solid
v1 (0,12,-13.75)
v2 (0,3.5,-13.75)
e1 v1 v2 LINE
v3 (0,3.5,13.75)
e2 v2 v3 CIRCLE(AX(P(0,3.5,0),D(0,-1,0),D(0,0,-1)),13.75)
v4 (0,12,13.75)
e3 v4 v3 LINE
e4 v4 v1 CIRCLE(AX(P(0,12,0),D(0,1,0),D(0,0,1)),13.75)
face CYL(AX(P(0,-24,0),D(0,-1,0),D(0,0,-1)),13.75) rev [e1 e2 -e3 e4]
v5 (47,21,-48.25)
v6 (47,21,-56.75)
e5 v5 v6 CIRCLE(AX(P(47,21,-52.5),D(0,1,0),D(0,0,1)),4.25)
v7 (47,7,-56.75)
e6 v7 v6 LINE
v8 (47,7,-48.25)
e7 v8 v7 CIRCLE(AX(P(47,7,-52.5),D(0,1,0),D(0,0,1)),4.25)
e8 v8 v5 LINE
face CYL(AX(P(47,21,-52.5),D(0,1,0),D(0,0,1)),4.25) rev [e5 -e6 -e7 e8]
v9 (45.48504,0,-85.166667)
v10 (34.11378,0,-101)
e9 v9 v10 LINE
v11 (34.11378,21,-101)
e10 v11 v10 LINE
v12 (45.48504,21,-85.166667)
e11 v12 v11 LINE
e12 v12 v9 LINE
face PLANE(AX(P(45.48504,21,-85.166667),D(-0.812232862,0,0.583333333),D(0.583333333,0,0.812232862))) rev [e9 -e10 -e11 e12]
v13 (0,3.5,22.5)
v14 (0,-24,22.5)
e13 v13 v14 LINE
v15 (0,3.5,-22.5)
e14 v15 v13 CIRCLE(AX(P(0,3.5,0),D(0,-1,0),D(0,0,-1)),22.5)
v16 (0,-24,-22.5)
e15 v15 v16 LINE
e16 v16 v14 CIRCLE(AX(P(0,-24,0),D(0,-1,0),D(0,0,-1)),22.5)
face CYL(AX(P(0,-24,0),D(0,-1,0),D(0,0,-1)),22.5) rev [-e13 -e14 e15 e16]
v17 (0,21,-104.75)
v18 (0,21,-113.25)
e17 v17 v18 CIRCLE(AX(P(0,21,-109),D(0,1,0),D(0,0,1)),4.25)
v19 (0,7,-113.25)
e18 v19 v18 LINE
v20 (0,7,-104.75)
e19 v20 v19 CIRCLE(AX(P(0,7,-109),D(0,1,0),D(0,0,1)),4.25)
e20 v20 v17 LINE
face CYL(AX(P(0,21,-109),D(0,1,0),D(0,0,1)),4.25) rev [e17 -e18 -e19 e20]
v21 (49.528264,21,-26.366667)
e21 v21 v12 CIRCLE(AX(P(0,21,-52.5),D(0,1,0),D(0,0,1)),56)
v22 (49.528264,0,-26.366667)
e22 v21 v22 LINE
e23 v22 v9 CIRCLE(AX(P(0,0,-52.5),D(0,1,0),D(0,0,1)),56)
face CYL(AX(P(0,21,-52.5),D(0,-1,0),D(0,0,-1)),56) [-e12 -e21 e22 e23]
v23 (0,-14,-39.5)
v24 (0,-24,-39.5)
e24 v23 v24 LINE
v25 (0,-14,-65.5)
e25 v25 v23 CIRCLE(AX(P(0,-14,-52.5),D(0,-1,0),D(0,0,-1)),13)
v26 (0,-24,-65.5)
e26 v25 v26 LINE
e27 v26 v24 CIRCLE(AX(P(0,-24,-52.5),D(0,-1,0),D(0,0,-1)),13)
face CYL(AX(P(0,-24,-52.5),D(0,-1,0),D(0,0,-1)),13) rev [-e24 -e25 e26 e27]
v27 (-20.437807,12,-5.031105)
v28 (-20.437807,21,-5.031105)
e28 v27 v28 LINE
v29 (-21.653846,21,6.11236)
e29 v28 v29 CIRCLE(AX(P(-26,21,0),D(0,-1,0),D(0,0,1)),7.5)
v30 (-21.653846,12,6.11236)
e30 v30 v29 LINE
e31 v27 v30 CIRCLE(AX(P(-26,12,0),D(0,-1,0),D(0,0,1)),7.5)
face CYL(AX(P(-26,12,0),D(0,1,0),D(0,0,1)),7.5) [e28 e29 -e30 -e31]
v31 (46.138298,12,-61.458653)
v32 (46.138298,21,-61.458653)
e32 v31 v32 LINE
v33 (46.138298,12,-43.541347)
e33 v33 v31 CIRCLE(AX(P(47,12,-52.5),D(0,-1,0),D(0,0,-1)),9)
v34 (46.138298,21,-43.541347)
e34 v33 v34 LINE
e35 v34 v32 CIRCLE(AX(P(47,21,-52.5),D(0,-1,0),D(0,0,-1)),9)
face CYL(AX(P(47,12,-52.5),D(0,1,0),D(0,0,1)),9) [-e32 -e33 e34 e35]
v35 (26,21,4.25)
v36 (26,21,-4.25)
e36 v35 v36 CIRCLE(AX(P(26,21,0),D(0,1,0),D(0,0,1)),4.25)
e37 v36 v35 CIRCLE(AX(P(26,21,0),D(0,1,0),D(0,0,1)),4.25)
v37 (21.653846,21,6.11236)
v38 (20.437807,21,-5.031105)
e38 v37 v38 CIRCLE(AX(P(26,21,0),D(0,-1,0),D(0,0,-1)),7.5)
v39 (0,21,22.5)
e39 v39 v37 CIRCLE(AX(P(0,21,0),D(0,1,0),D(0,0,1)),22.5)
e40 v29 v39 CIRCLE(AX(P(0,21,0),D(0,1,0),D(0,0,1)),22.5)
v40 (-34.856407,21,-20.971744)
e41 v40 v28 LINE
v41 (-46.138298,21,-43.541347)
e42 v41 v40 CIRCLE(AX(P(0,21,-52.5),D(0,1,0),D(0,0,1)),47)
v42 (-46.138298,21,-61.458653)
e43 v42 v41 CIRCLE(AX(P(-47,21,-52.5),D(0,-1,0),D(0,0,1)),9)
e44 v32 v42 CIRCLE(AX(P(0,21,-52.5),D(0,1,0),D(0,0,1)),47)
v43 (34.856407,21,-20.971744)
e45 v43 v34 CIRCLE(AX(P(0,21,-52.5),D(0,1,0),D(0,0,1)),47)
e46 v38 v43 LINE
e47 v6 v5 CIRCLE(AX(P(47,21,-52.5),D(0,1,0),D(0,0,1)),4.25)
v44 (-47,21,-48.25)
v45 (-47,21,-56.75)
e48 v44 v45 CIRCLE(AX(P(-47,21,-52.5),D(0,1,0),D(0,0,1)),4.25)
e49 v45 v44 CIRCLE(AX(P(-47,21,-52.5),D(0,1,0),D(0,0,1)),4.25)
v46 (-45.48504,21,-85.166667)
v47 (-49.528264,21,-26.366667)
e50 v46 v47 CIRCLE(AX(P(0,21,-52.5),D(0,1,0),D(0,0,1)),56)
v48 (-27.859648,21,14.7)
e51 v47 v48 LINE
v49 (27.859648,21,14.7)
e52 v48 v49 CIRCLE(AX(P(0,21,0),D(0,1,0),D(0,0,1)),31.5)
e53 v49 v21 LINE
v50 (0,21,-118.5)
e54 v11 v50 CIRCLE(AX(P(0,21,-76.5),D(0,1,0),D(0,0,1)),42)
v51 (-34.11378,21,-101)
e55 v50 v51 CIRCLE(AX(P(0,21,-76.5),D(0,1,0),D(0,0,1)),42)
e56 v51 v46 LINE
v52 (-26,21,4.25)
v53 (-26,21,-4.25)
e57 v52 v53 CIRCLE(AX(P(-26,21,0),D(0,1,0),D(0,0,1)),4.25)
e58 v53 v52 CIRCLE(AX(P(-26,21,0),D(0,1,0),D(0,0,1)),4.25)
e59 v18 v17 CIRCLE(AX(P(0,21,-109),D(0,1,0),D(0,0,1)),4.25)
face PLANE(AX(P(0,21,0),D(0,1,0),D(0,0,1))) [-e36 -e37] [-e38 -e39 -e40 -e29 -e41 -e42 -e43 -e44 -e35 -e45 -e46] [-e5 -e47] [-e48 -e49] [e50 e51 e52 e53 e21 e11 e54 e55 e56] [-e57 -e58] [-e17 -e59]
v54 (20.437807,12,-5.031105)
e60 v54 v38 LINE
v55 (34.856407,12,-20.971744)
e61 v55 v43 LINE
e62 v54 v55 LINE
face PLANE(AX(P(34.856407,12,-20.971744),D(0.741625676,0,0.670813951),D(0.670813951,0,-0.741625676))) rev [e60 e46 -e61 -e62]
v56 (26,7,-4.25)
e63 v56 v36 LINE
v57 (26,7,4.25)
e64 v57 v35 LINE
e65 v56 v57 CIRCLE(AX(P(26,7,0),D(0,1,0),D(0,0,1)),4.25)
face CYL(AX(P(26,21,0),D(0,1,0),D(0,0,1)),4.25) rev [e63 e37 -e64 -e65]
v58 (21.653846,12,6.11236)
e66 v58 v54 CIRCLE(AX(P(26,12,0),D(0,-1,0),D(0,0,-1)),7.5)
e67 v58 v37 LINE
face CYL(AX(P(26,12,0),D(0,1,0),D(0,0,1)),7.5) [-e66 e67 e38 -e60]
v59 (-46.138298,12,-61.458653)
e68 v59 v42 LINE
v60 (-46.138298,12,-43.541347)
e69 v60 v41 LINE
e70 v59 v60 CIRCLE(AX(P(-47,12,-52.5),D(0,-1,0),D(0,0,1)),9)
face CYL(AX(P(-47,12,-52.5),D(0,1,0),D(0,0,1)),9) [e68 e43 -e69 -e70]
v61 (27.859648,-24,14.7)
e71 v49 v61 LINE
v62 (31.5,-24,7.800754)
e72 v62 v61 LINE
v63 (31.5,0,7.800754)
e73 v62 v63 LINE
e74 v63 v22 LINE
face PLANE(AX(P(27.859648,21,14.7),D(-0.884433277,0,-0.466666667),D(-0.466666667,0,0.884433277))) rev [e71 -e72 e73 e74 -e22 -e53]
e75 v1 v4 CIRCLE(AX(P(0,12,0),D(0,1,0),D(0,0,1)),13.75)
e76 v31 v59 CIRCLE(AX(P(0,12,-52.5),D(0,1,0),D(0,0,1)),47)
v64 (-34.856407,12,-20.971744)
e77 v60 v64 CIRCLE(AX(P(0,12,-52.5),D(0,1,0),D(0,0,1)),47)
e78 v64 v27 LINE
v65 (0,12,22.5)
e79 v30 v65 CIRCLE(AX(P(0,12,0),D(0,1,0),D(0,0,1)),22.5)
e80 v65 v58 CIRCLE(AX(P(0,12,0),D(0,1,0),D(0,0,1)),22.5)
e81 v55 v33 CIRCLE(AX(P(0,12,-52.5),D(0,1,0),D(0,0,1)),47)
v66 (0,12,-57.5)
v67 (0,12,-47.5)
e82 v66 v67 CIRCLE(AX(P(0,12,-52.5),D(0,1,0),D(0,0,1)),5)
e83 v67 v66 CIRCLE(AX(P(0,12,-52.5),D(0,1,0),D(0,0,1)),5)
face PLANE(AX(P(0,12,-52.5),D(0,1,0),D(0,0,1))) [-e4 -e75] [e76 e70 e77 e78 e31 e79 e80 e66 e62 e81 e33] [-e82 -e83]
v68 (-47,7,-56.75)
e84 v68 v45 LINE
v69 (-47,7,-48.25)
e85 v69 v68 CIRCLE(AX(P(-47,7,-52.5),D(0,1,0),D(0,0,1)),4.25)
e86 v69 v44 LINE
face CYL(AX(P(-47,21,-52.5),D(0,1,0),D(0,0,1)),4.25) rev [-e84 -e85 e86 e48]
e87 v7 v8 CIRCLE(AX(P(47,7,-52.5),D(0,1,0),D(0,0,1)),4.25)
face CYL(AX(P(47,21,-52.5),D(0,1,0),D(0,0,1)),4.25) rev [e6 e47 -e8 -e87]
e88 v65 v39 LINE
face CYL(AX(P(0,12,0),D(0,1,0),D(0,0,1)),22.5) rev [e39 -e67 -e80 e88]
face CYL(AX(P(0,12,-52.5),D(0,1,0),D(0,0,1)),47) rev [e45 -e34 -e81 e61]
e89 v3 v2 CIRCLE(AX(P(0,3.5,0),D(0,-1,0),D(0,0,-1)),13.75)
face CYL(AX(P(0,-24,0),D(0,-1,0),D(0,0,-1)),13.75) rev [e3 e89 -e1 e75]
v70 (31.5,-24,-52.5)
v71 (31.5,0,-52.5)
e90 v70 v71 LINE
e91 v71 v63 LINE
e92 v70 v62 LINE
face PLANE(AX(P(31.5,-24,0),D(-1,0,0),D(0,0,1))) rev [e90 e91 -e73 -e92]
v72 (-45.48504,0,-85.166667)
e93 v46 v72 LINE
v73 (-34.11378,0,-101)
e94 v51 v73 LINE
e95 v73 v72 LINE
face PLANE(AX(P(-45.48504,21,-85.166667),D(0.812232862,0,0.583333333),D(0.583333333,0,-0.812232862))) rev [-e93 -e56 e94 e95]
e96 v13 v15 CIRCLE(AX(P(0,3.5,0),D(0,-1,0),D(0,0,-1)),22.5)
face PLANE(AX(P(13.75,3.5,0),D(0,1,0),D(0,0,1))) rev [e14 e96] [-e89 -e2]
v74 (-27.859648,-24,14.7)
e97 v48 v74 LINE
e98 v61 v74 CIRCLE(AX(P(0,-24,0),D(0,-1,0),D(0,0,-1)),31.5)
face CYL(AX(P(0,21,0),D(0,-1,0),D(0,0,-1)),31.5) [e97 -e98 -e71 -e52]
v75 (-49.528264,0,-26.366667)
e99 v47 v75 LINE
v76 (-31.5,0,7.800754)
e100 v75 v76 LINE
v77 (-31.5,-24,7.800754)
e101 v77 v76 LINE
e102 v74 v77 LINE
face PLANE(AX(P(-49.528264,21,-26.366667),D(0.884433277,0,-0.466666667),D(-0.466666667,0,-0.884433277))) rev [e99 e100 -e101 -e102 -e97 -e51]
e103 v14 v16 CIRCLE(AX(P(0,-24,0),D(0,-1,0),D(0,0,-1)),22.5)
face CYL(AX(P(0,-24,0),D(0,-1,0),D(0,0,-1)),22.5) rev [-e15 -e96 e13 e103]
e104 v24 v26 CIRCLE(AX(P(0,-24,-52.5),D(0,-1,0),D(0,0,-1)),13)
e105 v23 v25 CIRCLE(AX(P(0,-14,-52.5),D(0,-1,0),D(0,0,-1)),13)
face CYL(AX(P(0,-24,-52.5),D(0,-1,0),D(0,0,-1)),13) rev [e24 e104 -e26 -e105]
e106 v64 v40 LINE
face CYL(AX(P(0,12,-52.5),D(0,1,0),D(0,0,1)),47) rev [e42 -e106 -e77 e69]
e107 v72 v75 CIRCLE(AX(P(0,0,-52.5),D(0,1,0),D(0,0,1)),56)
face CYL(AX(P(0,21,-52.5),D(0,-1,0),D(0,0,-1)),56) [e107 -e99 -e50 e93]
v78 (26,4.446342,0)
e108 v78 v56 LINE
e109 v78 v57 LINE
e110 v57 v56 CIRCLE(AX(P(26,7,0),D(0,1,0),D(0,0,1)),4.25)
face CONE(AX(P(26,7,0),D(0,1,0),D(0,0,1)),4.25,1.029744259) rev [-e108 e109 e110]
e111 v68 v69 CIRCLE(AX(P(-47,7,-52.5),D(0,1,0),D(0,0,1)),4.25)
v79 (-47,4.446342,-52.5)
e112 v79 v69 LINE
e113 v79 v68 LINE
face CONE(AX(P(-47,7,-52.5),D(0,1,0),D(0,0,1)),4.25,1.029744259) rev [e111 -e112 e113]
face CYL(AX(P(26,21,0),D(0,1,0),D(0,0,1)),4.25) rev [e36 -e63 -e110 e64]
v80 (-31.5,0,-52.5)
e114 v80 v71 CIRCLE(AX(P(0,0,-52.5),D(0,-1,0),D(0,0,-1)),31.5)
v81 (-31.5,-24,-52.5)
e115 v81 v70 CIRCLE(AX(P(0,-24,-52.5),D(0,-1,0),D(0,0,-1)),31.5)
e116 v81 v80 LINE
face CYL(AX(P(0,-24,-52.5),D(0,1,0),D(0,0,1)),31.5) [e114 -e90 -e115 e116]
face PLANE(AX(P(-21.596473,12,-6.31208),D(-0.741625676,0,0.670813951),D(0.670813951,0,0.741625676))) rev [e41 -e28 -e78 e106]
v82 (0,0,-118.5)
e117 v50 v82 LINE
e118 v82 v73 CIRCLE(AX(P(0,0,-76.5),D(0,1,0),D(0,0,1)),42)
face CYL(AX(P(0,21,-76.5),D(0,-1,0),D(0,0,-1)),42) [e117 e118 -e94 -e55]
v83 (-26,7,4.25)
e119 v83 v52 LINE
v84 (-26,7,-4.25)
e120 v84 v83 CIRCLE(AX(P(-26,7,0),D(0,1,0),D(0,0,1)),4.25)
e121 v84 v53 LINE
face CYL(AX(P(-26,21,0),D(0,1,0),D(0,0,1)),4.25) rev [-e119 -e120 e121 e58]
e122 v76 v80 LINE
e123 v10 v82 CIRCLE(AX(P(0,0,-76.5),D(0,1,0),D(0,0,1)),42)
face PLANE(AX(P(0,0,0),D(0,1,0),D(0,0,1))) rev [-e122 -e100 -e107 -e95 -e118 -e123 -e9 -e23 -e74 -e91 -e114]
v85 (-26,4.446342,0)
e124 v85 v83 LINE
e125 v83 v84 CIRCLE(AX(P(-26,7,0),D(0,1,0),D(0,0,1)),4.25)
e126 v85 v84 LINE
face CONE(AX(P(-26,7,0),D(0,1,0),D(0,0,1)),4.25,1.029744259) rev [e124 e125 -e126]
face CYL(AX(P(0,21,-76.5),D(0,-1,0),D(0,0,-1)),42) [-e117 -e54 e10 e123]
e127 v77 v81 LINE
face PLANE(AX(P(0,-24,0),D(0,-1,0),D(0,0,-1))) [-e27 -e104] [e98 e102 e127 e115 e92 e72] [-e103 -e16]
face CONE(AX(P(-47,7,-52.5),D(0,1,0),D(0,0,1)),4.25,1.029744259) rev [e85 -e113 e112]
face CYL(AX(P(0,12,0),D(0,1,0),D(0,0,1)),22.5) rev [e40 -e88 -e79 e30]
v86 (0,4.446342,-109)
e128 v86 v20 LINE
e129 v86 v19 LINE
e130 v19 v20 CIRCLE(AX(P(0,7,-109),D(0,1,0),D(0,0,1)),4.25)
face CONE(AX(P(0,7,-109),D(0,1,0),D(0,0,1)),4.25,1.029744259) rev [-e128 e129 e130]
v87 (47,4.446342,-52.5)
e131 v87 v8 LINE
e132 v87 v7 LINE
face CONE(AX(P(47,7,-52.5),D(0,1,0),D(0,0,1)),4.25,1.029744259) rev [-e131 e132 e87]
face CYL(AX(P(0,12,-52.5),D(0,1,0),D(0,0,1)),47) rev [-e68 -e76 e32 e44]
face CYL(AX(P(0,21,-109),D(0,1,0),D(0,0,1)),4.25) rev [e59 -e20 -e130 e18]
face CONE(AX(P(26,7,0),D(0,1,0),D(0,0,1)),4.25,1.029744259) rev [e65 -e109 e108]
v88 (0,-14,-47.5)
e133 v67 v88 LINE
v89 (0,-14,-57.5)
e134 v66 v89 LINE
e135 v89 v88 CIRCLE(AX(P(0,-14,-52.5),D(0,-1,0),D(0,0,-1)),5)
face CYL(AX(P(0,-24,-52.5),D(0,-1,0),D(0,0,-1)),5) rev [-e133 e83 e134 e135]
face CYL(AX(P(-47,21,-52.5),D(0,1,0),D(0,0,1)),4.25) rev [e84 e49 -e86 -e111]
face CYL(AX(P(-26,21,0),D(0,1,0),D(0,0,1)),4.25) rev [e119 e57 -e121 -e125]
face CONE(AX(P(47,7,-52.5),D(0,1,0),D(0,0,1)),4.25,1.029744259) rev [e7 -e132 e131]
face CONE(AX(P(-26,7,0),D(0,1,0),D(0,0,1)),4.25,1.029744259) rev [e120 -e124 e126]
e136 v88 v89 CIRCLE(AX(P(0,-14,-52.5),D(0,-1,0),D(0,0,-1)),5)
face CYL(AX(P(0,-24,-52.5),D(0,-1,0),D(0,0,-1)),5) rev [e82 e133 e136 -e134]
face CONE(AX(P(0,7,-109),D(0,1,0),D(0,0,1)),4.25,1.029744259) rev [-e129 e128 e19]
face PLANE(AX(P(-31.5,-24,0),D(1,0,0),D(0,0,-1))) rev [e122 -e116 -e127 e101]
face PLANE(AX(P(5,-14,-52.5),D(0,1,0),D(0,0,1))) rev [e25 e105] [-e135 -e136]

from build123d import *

# Parameters (mm, degrees)
FLANGE_BASE_21MM_DEPTH               = 21
PORT_POCKET_9MM_DEEP_DEPTH           = 9
TAPPED_HOLE_M10_DRILL_8_5_D          = 8.5
TAPPED_HOLE_M10_DRILL_8_5_DEPTH      = 14
TAPPED_HOLE_M10_DRILL_8_5_TIP        = 2.553657631
PORT_START                           = 24
PORT_BOSS_24MM_DEPTH                 = 24
SECONDARY_PORT_C_BORE_10_D           = 10
SECONDARY_PORT_C_BORE_10_DEPTH       = 99.679486355
SECONDARY_PORT_C_BORE_10_CBORE_D     = 26
SECONDARY_PORT_C_BORE_10_CBORE_DEPTH = 10


with BuildPart() as part:
    # Flange Base Profile → Flange Base 21mm (new body)
    with BuildSketch(Plane(origin=(0, 0, 0), x_dir=(1, 0, 0), z_dir=(0, 1, 0))):
        with BuildLine():
            Line((-49.528263536, 26.366666667), (-27.859648239, -14.7))
            ThreePointArc((-27.859648239, -14.7), (0, -31.5), (27.859648239, -14.7))
            Line((27.859648239, -14.7), (49.528263536, 26.366666667))
            ThreePointArc((49.528263536, 26.366666667), (55.868076531, 56.341617458), (45.485040276, 85.166666667))
            Line((45.485040276, 85.166666667), (34.113780207, 101))
            ThreePointArc((34.113780207, 101), (0, 118.5), (-34.113780207, 101))
            Line((-34.113780207, 101), (-45.485040276, 85.166666667))
            ThreePointArc((-45.485040276, 85.166666667), (-55.868076531, 56.341617458), (-49.528263536, 26.366666667))
        make_face()
    extrude(amount=FLANGE_BASE_21MM_DEPTH)

    # Port Pocket Profile → Port Pocket 9mm Deep (cut)
    with BuildSketch(Plane(origin=(0, 21, 0), x_dir=(1, 0, 0), z_dir=(0, 1, 0))):
        with BuildLine():
            Line((-21.596473004, 6.312079988), (-20.437807431, 5.031104632))
            ThreePointArc((-20.437807431, 5.031104632), (-18.544261668, -0.813612883), (-21.653846154, -6.112360162))
            ThreePointArc((-21.653846154, -6.112360162), (0, -22.5), (21.653846154, -6.112360162))
            ThreePointArc((21.653846154, -6.112360162), (18.544261668, -0.813612883), (20.437807431, 5.031104632))
            Line((20.437807431, 5.031104632), (34.856406768, 20.971744304))
            ThreePointArc((34.856406768, 20.971744304), (42.040245988, 31.485297592), (46.138297872, 43.541346672))
            ThreePointArc((46.138297872, 43.541346672), (38, 52.5), (46.138297872, 61.458653328))
            ThreePointArc((46.138297872, 61.458653328), (0, 99.5), (-46.138297872, 61.458653328))
            ThreePointArc((-46.138297872, 61.458653328), (-38, 52.5), (-46.138297872, 43.541346672))
            ThreePointArc((-46.138297872, 43.541346672), (-42.040245988, 31.485297592), (-34.856406768, 20.971744304))
            Line((-34.856406768, 20.971744304), (-21.596473004, 6.312079988))
        make_face()
    extrude(amount=-PORT_POCKET_9MM_DEEP_DEPTH, mode=Mode.SUBTRACT)

    # Tapped Hole M10 Drill Ø8.5
    with Locations(Plane(origin=(0, 21, -109), x_dir=(0, 0, 1), z_dir=(0, 1, 0))):
        with Locations((0, 0), (56.5, -47), (56.5, 47), (109, -26), (109, 26)):
            Hole(TAPPED_HOLE_M10_DRILL_8_5_D / 2, depth=TAPPED_HOLE_M10_DRILL_8_5_DEPTH)
            with Locations((0, 0, -(TAPPED_HOLE_M10_DRILL_8_5_DEPTH + TAPPED_HOLE_M10_DRILL_8_5_TIP / 2))):  # 118° drill point
                Cone(0, TAPPED_HOLE_M10_DRILL_8_5_D / 2, TAPPED_HOLE_M10_DRILL_8_5_TIP, mode=Mode.SUBTRACT)

    # Port Boss Profile → Port Boss 24mm (add)
    with BuildSketch(Plane.XZ.offset(PORT_START)):
        with BuildLine():
            Line((31.5, 0), (31.5, -52.5))
            ThreePointArc((31.5, -52.5), (0, -84), (-31.5, -52.5))
            Line((-31.5, -52.5), (-31.5, 0))
            Line((-31.5, 0), (-31.5, 7.800753774))
            Line((-31.5, 7.800753774), (-27.859648239, 14.7))
            ThreePointArc((-27.859648239, 14.7), (0, 31.5), (27.859648239, 14.7))
            Line((27.859648239, 14.7), (31.5, 7.800753774))
            Line((31.5, 7.800753774), (31.5, 0))
        make_face()
    extrude(amount=-PORT_BOSS_24MM_DEPTH)

    # Sketch7 → Main Port C-Bore Ø27.5 (revolve, cut)
    with BuildSketch(Plane(origin=(0, -24, 0), x_dir=(0, 0, -1), z_dir=(1, 0, 0))):
        Polygon((0, 0), (0, 99.616451954), (13.75, 99.616451954), (13.75, 27.5), (22.5, 27.5), (22.5, 0), align=None)
    revolve(axis=Axis((0, 86, 0), (0, -1, 0)), mode=Mode.SUBTRACT)

    # Secondary Port C-Bore Ø10
    with Locations(Plane(origin=(0, -24, -52.5), x_dir=(0, 0, -1), z_dir=(0, -1, 0))):
        with Locations((0, 0)):
            CounterBoreHole(SECONDARY_PORT_C_BORE_10_D / 2, SECONDARY_PORT_C_BORE_10_CBORE_D / 2, SECONDARY_PORT_C_BORE_10_CBORE_DEPTH, depth=SECONDARY_PORT_C_BORE_10_DEPTH)


solid = part.part
